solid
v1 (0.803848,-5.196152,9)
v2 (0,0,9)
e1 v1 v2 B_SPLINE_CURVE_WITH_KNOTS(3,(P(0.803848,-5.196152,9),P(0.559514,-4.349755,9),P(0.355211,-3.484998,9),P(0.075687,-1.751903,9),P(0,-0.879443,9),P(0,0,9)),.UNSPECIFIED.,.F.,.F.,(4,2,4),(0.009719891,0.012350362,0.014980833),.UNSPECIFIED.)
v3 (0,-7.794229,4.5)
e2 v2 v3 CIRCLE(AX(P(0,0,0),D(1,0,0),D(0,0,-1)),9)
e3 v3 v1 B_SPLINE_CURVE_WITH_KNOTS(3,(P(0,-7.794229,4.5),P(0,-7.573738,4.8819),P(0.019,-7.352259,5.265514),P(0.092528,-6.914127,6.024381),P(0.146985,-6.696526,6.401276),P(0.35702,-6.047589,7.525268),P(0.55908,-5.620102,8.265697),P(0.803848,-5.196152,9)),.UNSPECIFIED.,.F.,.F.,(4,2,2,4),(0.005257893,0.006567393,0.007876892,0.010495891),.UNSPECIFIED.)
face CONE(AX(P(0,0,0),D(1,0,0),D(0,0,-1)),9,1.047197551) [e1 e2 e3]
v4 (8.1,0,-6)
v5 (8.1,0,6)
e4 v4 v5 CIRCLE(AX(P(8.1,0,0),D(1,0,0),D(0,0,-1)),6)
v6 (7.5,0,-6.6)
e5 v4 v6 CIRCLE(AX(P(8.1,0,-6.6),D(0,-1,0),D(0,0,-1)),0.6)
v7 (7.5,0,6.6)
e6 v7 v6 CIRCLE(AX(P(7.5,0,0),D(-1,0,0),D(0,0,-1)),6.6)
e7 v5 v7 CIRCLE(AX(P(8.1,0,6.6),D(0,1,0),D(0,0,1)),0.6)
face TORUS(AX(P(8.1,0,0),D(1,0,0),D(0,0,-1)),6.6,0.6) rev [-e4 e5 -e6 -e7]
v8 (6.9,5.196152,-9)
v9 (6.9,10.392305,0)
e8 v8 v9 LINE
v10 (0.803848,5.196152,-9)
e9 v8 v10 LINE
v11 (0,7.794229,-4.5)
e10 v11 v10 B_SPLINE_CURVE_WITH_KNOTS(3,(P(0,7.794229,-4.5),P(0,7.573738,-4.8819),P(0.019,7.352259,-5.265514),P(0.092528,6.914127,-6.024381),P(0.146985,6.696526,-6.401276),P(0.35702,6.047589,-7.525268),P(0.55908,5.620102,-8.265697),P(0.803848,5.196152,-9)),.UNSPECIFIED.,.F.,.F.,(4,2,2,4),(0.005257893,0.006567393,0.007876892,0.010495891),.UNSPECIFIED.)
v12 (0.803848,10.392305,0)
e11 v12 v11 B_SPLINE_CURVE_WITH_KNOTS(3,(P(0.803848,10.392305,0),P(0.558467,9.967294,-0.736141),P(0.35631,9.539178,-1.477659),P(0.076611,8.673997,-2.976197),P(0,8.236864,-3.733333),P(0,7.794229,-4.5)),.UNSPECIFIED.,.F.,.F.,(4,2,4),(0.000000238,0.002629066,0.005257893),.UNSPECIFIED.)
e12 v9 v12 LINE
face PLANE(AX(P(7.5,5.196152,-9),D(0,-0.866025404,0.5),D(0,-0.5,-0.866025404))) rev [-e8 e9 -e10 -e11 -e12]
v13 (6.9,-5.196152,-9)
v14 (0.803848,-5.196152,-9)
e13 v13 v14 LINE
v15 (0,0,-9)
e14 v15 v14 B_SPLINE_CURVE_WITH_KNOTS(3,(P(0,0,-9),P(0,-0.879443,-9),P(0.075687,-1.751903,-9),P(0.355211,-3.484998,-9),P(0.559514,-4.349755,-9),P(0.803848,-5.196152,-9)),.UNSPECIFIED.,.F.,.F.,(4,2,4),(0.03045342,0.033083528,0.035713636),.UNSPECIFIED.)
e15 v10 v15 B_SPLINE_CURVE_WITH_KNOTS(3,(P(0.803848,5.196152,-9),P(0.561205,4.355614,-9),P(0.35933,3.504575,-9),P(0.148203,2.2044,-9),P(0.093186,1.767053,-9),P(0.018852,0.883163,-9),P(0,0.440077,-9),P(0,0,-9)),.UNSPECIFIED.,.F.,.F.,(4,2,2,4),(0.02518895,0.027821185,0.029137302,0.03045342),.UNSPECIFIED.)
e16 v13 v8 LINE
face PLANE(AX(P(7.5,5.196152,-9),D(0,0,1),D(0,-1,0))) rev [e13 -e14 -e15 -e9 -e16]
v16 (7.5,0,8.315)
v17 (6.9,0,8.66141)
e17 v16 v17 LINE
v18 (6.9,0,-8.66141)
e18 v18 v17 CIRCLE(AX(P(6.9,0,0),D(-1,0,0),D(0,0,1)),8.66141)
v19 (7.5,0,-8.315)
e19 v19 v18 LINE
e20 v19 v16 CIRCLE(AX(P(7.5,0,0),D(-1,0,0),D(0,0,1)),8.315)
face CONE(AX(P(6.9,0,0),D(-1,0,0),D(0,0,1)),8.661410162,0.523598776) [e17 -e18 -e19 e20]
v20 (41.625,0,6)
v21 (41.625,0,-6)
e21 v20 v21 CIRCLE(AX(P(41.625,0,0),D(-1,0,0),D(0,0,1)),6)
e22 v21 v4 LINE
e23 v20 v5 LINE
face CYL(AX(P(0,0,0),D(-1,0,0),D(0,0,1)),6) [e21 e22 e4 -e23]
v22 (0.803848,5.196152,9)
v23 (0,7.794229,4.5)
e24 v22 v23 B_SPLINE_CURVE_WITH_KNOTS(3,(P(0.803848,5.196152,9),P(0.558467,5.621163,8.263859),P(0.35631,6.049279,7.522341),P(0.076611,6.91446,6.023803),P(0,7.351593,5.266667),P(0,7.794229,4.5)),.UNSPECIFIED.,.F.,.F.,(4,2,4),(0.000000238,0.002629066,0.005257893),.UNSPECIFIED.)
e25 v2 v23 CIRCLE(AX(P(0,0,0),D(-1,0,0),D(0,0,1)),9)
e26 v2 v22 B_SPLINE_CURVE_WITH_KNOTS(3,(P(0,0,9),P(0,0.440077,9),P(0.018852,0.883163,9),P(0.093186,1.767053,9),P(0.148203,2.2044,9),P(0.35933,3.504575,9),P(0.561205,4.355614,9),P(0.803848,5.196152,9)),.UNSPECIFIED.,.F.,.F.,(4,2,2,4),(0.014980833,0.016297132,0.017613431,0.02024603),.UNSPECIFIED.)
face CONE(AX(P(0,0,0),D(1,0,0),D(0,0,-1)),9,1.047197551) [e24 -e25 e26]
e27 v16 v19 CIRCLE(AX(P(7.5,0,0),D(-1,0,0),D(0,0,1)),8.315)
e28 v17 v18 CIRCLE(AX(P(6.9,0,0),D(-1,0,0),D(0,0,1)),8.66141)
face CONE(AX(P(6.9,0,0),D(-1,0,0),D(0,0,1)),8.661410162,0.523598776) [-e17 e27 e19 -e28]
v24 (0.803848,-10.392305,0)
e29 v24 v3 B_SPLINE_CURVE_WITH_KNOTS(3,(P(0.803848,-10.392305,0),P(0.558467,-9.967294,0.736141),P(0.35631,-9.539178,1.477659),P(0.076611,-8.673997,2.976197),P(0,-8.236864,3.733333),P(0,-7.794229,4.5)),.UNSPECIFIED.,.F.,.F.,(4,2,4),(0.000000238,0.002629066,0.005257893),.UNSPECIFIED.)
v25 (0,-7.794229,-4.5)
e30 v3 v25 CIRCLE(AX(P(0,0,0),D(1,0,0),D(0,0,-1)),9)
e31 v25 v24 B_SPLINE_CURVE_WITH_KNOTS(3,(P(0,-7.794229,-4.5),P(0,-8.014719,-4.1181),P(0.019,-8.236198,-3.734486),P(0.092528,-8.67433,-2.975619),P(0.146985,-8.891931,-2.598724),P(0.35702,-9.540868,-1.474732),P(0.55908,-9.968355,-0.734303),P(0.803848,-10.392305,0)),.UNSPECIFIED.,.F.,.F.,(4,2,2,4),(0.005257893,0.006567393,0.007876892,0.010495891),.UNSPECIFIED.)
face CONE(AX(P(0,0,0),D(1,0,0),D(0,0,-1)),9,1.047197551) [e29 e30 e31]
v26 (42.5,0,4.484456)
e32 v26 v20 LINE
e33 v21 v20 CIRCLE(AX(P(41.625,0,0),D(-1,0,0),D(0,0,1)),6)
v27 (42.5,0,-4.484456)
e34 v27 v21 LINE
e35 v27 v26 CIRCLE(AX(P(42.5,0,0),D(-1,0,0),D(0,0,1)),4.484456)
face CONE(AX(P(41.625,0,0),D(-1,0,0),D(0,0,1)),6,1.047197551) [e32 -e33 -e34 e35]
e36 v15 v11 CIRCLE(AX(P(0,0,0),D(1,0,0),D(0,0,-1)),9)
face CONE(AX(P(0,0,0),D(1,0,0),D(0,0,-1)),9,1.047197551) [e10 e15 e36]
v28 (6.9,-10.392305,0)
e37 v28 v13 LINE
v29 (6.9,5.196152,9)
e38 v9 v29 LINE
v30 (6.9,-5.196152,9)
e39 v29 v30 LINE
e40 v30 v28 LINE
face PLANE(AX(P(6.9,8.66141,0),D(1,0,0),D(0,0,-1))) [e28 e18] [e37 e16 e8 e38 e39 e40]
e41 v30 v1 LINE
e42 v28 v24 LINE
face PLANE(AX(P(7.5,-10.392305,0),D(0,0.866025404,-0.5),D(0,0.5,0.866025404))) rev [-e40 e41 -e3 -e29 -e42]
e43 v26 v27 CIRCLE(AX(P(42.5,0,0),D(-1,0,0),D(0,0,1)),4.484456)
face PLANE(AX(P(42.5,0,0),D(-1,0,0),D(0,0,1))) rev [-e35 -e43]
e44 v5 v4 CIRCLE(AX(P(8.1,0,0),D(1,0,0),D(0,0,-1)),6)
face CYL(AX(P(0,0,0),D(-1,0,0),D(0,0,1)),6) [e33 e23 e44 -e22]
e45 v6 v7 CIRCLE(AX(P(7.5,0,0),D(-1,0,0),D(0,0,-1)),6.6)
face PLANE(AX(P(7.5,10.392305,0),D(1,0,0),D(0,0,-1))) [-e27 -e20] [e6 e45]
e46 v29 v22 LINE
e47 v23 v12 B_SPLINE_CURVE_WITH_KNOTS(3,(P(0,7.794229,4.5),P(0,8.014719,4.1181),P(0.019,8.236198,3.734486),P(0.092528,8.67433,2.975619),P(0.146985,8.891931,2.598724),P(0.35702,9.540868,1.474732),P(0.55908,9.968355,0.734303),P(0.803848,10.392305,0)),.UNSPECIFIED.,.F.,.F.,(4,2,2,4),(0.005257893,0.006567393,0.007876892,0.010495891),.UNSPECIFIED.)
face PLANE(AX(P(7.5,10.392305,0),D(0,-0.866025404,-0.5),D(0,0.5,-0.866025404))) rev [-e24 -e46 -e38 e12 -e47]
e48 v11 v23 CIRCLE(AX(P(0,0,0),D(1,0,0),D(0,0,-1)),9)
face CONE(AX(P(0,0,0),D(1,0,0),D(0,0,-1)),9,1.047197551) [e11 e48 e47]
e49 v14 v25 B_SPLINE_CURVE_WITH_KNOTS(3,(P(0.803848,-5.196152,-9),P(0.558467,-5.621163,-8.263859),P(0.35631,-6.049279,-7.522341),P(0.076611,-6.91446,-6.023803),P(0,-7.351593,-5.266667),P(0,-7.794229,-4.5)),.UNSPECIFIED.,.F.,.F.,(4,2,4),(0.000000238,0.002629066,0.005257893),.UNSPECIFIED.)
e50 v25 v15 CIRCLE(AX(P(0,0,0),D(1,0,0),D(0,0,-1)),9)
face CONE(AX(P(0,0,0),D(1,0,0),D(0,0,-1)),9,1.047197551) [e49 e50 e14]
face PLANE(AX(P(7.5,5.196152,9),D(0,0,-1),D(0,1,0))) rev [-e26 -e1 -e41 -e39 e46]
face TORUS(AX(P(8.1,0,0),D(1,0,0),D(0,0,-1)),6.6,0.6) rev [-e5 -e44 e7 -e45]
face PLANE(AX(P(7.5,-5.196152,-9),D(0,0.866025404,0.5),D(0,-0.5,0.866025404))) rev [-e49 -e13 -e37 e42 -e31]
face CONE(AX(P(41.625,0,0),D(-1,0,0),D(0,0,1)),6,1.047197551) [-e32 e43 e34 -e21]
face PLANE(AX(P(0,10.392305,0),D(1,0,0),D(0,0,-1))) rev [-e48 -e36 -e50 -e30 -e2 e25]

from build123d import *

# Parameters (mm, degrees)
EXTRUDE_393_DEPTH = 7.5
FILLET_1265_R     = 0.6


with BuildPart() as part:
    # 草图1 → Extrude 393 (new body)
    with BuildSketch(Plane(origin=(0, 0, 0), x_dir=(0, 0, -1), z_dir=(1, 0, 0))):
        Polygon((9, 5.196152423), (9, -5.196152423), (0, -10.392304845), (-9, -5.196152423), (-9, 5.196152423), (0, 10.392304845), align=None)
    extrude(amount=EXTRUDE_393_DEPTH)

    # 草图2 → 凸台-旋转1 (revolve)
    with BuildSketch(Plane.XY, mode=Mode.PRIVATE) as revolve_1_sk:
        Polygon((0, 0), (42.5, 0), (42.5, 4.4845), (42.5, 6), (0, 6), align=None)
    revolve(revolve_1_sk.sketch.rotate(Axis((0, 0, 0), (1, 0, 0)), 90), axis=Axis((0, 0, 0), (1, 0, 0)))

    # 草图3 → 切除-旋转1 (revolve, cut)
    with BuildSketch(Plane.XY):
        Polygon((0, 9), (3.690598923, 15.392304845), (3.690598923, 20.392304845), (-10, 20.392304845), (-10, 9), align=None)
    revolve(axis=Axis((0, 0, 0), (1, 0, 0)), mode=Mode.SUBTRACT)

    # 草图4 → 切除-旋转3 (revolve, cut)
    with BuildSketch(Plane.XY, mode=Mode.PRIVATE) as cut_revolve_3_sk:
        Polygon((7.5, 8.315), (6.9, 8.661410162), (6.9, 10.392304845), (7.5, 10.392304845), align=None)
    revolve(cut_revolve_3_sk.sketch.rotate(Axis((0, 0, 0), (1, 0, 0)), 90), axis=Axis((0, 0, 0), (1, 0, 0)), mode=Mode.SUBTRACT)

    # Fillet 1265
    fillet_1265_edges = [part.edges().sort_by_distance(p)[0] for p in [
        (7.5, 0, -6),
    ]]
    fillet(fillet_1265_edges, radius=FILLET_1265_R)

    # 草图6 → 切除-旋转4 (revolve, cut)
    with BuildSketch(Plane.XY, mode=Mode.PRIVATE) as cut_revolve_4_sk:
        Polygon((41.625, 6), (43.375, 6), (42.5, 4.484455543), align=None)
    revolve(cut_revolve_4_sk.sketch.rotate(Axis((0, 0, 0), (1, 0, 0)), 90), axis=Axis((0, 0, 0), (1, 0, 0)), mode=Mode.SUBTRACT)


solid = part.part
